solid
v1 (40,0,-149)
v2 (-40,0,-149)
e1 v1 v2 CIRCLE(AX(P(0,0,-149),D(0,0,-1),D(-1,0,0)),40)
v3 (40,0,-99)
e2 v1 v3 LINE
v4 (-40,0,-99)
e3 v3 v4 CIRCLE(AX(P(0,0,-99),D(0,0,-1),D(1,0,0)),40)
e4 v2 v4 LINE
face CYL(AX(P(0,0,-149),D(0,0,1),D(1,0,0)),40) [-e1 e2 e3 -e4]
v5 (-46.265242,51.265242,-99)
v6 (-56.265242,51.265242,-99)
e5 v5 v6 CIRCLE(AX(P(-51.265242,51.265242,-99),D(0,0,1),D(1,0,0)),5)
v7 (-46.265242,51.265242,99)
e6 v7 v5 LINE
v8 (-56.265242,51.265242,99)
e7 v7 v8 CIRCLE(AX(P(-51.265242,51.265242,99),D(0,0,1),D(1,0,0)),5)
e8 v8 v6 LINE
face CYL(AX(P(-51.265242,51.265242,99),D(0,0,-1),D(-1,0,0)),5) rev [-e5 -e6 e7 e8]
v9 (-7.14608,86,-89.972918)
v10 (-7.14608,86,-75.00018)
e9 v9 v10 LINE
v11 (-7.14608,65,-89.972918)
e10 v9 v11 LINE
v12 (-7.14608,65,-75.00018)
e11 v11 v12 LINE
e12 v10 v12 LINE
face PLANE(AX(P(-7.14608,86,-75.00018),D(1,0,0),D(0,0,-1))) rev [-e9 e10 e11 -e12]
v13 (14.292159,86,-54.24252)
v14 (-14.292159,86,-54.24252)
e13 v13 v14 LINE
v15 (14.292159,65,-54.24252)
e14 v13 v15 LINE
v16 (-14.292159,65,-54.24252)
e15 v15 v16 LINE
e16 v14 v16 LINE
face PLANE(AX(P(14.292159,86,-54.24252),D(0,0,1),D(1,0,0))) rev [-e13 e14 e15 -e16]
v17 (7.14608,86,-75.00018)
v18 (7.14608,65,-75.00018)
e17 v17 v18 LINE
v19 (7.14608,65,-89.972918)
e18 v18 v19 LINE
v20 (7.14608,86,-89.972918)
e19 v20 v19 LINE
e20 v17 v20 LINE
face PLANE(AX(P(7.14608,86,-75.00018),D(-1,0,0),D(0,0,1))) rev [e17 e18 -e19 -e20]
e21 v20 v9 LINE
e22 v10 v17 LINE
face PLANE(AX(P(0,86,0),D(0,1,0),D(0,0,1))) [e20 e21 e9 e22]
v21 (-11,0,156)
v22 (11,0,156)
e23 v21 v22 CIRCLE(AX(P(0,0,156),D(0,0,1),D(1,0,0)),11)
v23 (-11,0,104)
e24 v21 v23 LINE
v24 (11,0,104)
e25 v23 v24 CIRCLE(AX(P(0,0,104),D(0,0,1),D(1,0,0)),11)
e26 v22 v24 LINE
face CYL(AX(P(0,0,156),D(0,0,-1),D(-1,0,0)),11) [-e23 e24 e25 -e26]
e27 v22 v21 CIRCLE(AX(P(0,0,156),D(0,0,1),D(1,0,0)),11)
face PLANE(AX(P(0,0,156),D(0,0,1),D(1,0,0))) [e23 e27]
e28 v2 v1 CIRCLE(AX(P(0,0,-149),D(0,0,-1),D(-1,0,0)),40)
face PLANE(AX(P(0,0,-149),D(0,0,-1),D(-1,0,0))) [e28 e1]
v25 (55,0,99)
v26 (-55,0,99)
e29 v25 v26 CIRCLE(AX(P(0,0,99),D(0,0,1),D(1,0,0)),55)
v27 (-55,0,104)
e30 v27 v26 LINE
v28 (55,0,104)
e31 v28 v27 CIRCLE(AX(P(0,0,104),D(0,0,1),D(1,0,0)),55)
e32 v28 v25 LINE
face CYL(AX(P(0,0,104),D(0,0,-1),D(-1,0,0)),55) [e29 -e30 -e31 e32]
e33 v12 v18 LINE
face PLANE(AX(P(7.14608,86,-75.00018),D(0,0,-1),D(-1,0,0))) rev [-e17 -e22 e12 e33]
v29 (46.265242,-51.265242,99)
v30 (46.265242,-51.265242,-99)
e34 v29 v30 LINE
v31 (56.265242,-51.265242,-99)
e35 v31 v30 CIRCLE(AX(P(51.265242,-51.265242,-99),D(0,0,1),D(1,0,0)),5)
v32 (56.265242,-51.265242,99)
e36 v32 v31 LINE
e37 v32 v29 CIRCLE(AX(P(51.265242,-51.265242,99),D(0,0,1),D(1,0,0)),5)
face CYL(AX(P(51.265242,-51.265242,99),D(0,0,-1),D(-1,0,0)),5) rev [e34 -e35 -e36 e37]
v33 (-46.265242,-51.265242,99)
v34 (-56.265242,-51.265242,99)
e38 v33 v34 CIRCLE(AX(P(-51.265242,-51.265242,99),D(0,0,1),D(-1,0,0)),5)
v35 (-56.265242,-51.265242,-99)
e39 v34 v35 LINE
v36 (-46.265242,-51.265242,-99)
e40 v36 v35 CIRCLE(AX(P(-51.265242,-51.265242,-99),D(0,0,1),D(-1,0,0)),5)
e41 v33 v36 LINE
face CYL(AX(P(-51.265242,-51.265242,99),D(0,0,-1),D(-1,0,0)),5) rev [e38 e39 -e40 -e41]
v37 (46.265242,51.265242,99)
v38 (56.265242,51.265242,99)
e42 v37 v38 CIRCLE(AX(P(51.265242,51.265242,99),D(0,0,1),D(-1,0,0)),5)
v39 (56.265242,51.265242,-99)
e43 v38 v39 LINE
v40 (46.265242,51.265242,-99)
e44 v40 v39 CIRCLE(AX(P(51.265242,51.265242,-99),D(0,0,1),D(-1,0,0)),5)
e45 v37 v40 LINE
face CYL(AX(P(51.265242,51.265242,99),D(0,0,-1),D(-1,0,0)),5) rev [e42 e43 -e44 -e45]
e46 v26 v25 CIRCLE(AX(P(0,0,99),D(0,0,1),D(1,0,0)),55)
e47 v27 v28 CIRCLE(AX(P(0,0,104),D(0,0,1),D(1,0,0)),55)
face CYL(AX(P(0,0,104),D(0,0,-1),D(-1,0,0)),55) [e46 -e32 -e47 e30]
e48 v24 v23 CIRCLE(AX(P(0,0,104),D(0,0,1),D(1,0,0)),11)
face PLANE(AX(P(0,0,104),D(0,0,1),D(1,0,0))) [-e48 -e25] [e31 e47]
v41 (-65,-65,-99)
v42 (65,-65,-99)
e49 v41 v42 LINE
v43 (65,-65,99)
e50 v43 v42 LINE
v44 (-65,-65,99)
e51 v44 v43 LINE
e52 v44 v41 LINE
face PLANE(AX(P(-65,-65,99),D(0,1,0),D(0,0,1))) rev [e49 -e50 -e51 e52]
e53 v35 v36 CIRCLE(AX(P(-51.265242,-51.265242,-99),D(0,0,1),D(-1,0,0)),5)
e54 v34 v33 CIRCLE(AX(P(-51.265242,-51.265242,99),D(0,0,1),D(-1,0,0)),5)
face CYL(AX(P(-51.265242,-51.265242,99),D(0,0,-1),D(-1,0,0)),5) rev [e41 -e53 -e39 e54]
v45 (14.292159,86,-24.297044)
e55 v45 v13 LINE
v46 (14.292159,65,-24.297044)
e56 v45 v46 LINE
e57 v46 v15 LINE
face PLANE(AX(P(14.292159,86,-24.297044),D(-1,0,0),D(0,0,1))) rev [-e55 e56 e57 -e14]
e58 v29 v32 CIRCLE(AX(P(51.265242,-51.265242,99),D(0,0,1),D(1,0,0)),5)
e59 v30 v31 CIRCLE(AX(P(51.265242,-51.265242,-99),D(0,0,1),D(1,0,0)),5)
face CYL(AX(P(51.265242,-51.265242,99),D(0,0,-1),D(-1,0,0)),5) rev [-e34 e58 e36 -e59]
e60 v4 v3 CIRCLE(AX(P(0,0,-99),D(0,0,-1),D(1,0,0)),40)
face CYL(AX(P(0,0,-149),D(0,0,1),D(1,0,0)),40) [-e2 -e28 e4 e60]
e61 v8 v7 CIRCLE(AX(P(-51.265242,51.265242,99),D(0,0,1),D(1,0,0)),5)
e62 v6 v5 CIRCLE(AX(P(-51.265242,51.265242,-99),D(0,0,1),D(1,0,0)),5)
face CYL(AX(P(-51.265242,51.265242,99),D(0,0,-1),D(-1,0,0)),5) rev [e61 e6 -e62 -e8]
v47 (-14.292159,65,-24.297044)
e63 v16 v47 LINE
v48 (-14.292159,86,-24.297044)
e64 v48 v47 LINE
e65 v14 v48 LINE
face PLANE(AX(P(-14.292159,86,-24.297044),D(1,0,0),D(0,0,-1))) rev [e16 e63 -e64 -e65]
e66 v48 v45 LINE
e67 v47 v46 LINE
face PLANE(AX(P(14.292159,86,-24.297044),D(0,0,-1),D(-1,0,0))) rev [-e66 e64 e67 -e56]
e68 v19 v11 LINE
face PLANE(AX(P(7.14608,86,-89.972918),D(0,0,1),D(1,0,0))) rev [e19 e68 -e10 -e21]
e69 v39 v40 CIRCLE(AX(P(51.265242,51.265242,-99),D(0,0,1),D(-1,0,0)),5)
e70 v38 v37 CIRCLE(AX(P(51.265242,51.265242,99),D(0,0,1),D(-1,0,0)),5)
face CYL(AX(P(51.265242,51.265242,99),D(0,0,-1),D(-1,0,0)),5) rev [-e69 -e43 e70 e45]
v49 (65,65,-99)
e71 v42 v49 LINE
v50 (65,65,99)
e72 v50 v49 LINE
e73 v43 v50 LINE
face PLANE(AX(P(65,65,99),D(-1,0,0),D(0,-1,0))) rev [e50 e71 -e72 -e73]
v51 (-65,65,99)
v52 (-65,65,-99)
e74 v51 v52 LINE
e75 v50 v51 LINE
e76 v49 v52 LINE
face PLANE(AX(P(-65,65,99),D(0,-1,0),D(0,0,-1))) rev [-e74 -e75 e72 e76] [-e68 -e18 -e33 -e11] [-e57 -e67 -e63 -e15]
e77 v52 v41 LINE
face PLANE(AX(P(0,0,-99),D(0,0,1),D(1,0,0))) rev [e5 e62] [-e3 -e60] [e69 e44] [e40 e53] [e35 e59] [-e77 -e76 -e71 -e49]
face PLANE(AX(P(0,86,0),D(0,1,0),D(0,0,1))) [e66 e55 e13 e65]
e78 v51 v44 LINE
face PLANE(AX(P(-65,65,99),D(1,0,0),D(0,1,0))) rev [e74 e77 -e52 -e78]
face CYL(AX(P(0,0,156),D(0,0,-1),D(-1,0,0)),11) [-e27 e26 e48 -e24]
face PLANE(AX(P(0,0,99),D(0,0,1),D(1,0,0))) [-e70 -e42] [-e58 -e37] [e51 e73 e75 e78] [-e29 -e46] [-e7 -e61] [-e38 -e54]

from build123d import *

# Parameters (mm, degrees)
SKETCH_1_W      = 130
SKETCH_1_H      = 130
SKETCH_1_R      = 5
EXTRUDE_1_DEPTH = 99
SKETCH_2_R      = 55
EXTRUDE_2_DEPTH = 5
SKETCH_3_R      = 11
EXTRUDE_3_DEPTH = 52
SKETCH_5_W      = 28.58431815
SKETCH_5_H      = 29.945476157
SKETCH_5_W_2    = 14.292159074
SKETCH_5_H_2    = 14.972738078
EXTRUDE_4_DEPTH = 86
SKETCH_6_R      = 40
EXTRUDE_5_DEPTH = 50


with BuildPart() as part:
    # 草图1 → 凸台-拉伸1 (new, symmetric)
    with BuildSketch(Plane.XY):
        Rectangle(SKETCH_1_W, SKETCH_1_H)
        with Locations((-51.265241636, 51.265241636)):
            Circle(SKETCH_1_R, mode=Mode.SUBTRACT)
        with Locations(Location((51.265241636, 51.265241636, 0), (0, 0, 180))):
            Circle(SKETCH_1_R, mode=Mode.SUBTRACT)
        with Locations(Location((-51.265241636, -51.265241636, 0), (0, 0, 180))):
            Circle(SKETCH_1_R, mode=Mode.SUBTRACT)
        with Locations((51.265241636, -51.265241636)):
            Circle(SKETCH_1_R, mode=Mode.SUBTRACT)
    extrude(amount=EXTRUDE_1_DEPTH, both=True)

    # 草图2 → 凸台-拉伸2 (add)
    with BuildSketch(Plane.XY.offset(99)):
        Circle(SKETCH_2_R)
    extrude(amount=EXTRUDE_2_DEPTH)

    # 草图3 → 凸台-拉伸3 (add)
    with BuildSketch(Plane.XY.offset(104)):
        with Locations(Location((0, 0, 0), (0, 0, 180))):
            Circle(SKETCH_3_R)
    extrude(amount=EXTRUDE_3_DEPTH)

    # 草图5 → 凸台-拉伸4 (add)
    with BuildSketch(Plane(origin=(0, 0, 0), x_dir=(1, 0, 0), z_dir=(0, 1, 0))):
        with Locations((0, 39.269782118)):
            Rectangle(SKETCH_5_W, SKETCH_5_H)
        with Locations((0, 82.486548844)):
            Rectangle(SKETCH_5_W_2, SKETCH_5_H_2)
    extrude(amount=EXTRUDE_4_DEPTH)

    # 草图6 → 凸台-拉伸5 (add)
    with BuildSketch(Plane(origin=(0, 0, -99), x_dir=(-1, 0, 0), z_dir=(0, 0, -1))):
        with Locations(Location((0, 0, 0), (0, 0, 180))):
            Circle(SKETCH_6_R)
    extrude(amount=EXTRUDE_5_DEPTH)


solid = part.part
